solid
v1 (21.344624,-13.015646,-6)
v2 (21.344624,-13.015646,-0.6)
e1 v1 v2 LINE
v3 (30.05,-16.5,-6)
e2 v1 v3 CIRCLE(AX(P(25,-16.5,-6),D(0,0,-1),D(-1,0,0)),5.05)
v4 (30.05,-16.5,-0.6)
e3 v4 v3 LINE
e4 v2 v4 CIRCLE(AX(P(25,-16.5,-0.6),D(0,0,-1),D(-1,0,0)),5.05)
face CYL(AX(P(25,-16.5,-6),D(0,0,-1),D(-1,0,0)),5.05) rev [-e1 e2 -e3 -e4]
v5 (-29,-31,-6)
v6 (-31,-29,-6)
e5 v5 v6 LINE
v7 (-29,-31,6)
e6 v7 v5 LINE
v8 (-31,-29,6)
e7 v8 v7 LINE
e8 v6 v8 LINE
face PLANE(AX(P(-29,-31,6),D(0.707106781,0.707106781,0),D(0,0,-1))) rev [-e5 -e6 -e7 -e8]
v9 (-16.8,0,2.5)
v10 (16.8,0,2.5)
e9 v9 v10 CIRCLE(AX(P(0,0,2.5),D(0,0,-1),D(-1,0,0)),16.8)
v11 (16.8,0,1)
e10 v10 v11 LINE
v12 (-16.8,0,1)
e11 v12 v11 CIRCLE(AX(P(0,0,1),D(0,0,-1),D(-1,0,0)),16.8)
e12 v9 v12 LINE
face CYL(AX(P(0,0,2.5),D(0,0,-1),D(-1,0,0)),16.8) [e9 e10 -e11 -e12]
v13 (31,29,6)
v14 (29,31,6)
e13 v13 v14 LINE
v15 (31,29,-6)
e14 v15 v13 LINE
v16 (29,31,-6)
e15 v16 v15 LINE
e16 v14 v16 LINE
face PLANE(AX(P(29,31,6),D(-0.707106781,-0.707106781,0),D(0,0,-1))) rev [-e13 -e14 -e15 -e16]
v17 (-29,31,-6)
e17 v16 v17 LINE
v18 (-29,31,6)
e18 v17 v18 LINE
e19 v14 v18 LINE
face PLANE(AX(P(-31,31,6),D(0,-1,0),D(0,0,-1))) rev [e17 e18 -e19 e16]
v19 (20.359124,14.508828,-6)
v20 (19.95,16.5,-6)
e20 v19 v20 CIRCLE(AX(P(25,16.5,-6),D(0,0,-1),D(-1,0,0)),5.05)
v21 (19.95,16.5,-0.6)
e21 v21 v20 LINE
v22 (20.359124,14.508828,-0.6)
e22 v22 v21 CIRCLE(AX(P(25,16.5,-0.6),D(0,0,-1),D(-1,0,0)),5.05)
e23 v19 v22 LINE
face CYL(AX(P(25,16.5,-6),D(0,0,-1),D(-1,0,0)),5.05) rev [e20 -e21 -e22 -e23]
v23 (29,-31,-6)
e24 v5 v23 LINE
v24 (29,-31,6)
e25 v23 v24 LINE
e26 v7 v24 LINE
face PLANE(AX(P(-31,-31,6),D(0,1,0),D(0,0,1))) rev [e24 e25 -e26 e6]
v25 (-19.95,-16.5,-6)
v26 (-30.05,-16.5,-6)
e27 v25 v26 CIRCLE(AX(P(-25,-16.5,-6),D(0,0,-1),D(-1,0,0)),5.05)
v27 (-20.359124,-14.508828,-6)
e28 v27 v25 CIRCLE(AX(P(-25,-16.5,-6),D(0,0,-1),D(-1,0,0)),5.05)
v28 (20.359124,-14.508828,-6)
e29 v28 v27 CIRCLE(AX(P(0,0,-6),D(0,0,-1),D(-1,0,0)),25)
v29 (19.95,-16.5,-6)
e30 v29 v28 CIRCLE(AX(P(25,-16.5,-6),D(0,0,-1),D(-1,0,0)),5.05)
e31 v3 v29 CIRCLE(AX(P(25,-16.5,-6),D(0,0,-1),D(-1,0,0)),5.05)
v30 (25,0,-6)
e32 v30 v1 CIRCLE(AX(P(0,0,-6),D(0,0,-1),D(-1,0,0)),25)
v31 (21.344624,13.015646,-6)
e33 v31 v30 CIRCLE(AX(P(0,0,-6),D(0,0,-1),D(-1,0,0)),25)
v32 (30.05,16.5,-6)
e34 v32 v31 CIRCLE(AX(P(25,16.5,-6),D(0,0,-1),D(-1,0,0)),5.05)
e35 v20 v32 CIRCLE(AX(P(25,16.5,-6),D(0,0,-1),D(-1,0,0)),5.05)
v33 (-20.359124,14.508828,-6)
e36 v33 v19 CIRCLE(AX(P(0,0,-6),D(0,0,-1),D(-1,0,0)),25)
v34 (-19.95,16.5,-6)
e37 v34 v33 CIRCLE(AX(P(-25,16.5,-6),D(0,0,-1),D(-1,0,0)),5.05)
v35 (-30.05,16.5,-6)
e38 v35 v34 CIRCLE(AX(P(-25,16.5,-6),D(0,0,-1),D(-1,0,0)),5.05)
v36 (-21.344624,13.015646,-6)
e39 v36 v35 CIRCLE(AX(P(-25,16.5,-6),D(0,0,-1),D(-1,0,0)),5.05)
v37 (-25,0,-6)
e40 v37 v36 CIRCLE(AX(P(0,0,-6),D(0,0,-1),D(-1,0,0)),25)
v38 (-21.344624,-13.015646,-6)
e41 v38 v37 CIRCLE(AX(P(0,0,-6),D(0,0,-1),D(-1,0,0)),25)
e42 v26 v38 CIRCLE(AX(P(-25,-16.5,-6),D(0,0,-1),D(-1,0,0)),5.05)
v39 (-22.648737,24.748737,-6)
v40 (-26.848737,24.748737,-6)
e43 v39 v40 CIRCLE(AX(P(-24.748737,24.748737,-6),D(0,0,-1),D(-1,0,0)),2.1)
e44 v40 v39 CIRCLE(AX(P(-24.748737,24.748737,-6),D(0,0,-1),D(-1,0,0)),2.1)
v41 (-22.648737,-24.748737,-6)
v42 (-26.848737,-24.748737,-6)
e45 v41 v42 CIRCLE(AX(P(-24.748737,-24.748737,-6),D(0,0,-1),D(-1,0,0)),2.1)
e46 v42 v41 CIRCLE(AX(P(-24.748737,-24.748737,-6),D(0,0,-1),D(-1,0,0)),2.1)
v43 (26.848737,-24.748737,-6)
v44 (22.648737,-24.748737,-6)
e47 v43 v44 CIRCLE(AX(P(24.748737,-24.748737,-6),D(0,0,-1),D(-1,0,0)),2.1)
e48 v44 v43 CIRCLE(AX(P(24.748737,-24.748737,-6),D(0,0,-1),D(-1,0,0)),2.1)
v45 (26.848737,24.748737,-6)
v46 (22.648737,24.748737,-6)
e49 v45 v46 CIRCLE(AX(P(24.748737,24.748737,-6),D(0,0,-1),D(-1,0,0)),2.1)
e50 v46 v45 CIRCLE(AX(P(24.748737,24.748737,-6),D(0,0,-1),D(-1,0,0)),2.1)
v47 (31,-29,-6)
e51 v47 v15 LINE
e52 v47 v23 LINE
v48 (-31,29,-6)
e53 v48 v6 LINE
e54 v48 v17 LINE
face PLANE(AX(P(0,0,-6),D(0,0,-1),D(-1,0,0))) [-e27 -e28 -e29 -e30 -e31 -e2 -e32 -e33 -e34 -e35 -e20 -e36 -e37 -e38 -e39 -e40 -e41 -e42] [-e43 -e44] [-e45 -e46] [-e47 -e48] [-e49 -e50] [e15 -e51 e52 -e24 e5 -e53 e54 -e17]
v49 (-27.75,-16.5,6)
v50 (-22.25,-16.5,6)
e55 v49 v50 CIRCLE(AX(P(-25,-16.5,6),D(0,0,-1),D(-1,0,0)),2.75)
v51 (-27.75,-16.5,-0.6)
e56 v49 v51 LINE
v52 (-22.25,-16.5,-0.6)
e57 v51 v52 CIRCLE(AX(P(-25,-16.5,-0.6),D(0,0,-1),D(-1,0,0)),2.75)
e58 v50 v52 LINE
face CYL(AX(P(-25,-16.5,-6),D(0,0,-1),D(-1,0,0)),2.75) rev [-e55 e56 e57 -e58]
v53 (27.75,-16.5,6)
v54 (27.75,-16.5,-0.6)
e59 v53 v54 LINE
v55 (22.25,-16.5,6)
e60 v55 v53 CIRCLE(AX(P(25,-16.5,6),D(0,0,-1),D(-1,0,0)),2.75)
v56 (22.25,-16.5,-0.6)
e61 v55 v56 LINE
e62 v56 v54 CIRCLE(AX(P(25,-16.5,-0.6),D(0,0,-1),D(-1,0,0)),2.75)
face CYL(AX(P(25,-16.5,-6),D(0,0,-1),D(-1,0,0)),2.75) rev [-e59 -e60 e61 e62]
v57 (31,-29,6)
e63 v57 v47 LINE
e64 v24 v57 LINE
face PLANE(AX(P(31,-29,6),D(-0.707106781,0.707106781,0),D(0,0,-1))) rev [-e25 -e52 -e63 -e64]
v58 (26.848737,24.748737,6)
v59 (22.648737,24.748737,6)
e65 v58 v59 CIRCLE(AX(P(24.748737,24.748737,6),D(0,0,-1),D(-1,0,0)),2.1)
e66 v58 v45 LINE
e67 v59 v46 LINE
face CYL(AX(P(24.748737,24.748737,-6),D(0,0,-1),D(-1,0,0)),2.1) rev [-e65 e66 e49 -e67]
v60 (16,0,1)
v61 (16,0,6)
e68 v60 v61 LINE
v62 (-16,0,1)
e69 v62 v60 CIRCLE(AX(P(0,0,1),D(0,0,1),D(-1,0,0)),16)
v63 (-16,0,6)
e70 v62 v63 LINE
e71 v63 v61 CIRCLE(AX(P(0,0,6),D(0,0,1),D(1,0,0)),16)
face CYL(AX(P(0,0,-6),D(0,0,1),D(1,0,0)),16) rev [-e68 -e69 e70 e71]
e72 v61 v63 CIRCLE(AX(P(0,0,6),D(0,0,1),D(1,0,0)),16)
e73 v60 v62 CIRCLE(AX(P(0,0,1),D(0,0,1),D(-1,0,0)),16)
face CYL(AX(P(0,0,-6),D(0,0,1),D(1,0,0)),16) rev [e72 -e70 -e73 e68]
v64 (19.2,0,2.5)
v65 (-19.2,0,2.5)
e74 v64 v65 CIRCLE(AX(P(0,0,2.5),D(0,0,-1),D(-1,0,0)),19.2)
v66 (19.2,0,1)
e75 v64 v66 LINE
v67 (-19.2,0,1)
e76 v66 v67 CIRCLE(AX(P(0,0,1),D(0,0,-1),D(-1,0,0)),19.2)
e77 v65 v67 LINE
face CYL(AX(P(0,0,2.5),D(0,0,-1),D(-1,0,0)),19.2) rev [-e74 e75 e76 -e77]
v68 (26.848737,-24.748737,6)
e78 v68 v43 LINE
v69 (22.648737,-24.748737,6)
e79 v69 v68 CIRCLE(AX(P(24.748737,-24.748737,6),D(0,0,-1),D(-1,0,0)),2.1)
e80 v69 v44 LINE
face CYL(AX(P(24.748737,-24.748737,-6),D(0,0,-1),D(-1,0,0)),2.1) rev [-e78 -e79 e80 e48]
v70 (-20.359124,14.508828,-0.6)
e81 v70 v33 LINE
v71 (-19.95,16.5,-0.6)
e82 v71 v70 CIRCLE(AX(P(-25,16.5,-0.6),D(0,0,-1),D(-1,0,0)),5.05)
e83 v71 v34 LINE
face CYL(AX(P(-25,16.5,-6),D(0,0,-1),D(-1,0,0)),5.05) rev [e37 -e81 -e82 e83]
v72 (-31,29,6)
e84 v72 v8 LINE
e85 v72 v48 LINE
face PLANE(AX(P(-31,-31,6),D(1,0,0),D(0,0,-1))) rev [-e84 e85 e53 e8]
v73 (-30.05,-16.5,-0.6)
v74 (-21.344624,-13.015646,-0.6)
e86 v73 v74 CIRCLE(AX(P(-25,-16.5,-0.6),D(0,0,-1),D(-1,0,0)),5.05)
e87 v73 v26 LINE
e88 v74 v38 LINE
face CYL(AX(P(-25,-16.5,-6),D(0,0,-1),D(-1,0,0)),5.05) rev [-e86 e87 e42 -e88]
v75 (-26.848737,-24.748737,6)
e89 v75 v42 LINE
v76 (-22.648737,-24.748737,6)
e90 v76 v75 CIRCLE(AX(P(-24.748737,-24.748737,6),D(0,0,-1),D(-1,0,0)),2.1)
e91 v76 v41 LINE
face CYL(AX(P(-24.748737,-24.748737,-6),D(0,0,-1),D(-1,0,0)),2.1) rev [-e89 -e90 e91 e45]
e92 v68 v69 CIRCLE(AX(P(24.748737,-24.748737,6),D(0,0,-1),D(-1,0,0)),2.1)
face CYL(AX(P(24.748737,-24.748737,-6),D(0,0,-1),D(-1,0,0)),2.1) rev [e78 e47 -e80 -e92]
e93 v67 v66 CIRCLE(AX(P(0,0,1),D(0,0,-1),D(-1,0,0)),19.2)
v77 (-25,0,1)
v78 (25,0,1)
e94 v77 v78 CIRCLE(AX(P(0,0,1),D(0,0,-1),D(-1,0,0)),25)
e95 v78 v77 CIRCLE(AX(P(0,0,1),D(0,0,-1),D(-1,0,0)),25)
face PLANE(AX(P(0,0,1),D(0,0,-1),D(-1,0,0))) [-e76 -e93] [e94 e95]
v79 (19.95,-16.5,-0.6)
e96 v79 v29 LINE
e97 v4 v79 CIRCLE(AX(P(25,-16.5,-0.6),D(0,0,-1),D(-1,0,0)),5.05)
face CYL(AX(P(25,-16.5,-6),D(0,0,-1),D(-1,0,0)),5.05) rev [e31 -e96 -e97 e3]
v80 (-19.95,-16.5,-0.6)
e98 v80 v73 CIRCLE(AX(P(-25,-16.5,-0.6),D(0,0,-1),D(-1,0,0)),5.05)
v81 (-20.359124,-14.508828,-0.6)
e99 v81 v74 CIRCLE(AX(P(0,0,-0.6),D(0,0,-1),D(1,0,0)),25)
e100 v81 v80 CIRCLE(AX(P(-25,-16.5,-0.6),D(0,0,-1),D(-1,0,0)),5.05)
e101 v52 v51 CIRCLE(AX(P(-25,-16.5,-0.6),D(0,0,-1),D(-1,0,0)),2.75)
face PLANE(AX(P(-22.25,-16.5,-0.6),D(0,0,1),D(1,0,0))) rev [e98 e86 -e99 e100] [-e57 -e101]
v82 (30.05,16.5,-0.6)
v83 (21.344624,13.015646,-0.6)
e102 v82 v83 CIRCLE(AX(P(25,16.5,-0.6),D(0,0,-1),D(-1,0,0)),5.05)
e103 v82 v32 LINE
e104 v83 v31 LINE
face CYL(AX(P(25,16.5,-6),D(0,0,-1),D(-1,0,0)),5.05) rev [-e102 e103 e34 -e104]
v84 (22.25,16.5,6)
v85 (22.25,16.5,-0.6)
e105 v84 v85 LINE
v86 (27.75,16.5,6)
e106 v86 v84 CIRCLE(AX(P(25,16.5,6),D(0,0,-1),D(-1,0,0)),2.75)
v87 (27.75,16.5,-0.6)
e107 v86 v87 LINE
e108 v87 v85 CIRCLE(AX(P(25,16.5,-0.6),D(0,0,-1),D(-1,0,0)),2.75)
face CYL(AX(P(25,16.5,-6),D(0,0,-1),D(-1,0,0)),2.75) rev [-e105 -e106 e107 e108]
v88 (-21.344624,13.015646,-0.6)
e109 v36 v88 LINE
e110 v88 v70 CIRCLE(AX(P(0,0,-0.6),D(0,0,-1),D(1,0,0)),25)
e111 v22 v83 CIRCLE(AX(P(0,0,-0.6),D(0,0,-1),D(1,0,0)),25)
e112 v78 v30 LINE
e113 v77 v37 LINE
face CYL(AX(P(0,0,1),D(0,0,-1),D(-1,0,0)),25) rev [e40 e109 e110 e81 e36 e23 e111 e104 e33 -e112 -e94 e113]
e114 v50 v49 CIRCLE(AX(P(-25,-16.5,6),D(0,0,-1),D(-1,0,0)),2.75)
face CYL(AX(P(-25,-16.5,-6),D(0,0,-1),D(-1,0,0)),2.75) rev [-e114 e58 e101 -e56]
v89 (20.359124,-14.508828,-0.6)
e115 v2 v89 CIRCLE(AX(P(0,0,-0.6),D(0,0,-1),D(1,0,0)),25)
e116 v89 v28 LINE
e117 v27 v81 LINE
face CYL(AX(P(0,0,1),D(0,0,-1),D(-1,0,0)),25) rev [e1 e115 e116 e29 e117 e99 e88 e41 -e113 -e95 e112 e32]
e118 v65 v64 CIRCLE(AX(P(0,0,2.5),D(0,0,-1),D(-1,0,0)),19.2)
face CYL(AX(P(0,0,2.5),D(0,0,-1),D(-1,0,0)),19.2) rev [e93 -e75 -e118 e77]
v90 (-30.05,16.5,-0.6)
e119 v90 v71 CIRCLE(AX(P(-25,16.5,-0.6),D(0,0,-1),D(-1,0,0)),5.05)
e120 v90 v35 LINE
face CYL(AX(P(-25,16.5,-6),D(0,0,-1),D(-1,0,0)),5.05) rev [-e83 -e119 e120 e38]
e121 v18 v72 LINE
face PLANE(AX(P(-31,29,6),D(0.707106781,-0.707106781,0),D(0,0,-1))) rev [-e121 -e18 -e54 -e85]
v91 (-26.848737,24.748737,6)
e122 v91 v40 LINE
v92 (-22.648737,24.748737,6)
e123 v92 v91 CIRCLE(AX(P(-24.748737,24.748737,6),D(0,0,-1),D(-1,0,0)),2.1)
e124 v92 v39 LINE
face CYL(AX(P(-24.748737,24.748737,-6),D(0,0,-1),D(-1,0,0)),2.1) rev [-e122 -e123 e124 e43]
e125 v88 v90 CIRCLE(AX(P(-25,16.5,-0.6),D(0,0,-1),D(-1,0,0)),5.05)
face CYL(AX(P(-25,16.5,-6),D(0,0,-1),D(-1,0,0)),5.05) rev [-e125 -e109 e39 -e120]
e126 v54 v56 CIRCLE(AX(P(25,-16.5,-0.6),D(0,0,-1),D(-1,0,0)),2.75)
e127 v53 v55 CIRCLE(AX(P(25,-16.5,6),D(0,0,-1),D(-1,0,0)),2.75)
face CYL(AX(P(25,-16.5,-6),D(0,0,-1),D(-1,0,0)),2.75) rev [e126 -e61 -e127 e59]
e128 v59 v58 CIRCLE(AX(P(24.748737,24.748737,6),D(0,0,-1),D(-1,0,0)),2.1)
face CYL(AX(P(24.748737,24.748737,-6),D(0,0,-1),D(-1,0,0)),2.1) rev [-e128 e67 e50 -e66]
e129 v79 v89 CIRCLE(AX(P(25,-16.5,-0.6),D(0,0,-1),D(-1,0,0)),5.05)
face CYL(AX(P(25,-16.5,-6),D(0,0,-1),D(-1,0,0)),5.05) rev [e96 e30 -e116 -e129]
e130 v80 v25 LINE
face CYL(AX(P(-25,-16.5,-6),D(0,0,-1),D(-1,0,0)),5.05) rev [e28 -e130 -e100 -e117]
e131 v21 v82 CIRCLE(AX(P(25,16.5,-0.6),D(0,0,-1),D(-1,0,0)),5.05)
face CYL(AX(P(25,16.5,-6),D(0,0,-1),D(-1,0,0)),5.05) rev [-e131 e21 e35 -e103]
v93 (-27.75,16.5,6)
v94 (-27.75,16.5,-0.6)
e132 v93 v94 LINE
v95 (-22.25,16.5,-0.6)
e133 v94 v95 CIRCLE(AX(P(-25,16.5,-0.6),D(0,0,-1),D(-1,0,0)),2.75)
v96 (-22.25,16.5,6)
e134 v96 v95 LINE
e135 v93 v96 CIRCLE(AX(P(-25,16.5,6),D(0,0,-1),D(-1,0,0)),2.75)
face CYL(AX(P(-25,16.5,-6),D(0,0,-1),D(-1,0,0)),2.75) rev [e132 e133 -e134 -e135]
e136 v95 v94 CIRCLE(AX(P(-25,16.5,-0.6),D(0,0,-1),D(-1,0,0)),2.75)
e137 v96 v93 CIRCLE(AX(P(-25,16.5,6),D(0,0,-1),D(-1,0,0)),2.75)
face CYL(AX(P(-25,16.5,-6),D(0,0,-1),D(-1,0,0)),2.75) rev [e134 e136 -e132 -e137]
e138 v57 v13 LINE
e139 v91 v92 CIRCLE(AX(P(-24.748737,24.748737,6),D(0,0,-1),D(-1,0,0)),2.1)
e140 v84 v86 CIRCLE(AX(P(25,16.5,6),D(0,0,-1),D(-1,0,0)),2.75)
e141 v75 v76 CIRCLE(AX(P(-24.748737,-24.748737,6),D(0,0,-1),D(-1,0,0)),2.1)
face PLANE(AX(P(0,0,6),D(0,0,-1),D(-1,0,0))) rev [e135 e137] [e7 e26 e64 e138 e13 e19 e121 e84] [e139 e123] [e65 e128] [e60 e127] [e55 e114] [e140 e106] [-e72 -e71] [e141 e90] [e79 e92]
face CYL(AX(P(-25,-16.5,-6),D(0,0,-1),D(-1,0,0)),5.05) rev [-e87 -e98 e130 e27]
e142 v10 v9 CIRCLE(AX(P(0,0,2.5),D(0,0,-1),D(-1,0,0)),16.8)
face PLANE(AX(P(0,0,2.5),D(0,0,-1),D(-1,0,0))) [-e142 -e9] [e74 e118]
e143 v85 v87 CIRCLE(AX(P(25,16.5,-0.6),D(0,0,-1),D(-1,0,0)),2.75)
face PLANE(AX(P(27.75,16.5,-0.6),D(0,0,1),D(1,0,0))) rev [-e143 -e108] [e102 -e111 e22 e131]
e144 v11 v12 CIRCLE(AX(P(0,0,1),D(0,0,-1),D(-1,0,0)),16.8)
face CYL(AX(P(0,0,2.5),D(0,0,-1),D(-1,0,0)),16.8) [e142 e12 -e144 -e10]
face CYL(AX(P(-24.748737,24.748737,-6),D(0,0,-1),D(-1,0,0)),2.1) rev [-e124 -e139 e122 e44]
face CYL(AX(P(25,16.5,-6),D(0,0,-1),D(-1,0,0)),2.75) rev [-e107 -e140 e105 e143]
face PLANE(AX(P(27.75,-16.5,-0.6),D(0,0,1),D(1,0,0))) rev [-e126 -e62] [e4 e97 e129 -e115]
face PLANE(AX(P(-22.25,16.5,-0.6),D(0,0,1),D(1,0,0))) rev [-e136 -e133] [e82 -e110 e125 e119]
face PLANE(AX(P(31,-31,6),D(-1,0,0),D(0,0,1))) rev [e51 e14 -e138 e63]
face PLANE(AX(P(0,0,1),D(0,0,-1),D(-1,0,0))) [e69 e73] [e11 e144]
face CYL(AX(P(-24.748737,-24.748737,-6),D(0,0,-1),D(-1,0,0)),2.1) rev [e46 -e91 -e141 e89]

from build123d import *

# Parameters (mm, degrees)
SKETCH_1_W                     = 62
SKETCH_1_H                     = 62
EXTRUDE_1_DEPTH                = 6
SKETCH_2_R                     = 16
CUT_EXTRUDE_1_DEPTH            = 46.453272709
HOLE_WIZARD_M5_1_D             = 4.2
SKETCH_11_R                    = 25
CUT_EXTRUDE_2_DEPTH            = 7
HOLE_WIZARD_M5_1_2_D           = 5.5
HOLE_WIZARD_M5_1_2_CBORE_D     = 10.1
HOLE_WIZARD_M5_1_2_CBORE_DEPTH = 5.4
CHAMFER_1_SIZE                 = 2
SKETCH_13_R                    = 19.2
SKETCH_13_R_2                  = 16.8
CUT_EXTRUDE_3_DEPTH            = 1.5


with BuildPart() as part:
    # 草图1 → 凸台-拉伸1 (new, symmetric)
    with BuildSketch(Plane.XY):
        Rectangle(SKETCH_1_W, SKETCH_1_H)
    extrude(amount=EXTRUDE_1_DEPTH, both=True)

    # 草图2 → 切除-拉伸1 (cut, through all)
    with BuildSketch(Plane.XY.offset(6)):
        Circle(SKETCH_2_R)
    extrude(amount=-CUT_EXTRUDE_1_DEPTH, mode=Mode.SUBTRACT)

    # Hole Wizard M5 _1 (through all)
    with Locations(Plane(origin=(0, 0, -6), x_dir=(1, 0, 0), z_dir=(0, 0, -1))):
        with Locations((-24.748737342, -24.748737342), (24.748737342, -24.748737342), (-24.748737342, 24.748737342), (24.748737342, 24.748737342)):
            Hole(HOLE_WIZARD_M5_1_D / 2)

    # 草图11 → 切除-拉伸2 (cut)
    with BuildSketch(Plane(origin=(0, 0, -6), x_dir=(-1, 0, 0), z_dir=(0, 0, -1))):
        Circle(SKETCH_11_R)
    extrude(amount=-CUT_EXTRUDE_2_DEPTH, mode=Mode.SUBTRACT)

    # Hole Wizard M5 _1 2 (through all)
    with Locations(Plane(origin=(0, 0, -6), x_dir=(-1, 0, 0), z_dir=(0, 0, -1))):
        with Locations((-25, 16.5), (25, 16.5), (25, -16.5), (-25, -16.5)):
            CounterBoreHole(HOLE_WIZARD_M5_1_2_D / 2, HOLE_WIZARD_M5_1_2_CBORE_D / 2, HOLE_WIZARD_M5_1_2_CBORE_DEPTH)

    # 倒角1
    chamfer_1_edges = [part.edges().sort_by_distance(p)[0] for p in [
        (31, -31, 0),
        (-31, -31, 0),
        (-31, 31, 0),
        (31, 31, 0),
    ]]
    chamfer(chamfer_1_edges, length=CHAMFER_1_SIZE)

    # 草图13 → 切除-拉伸3 (cut)
    with BuildSketch(Plane(origin=(0, 0, 1), x_dir=(-1, 0, 0), z_dir=(0, 0, -1))):
        Circle(SKETCH_13_R)
        Circle(SKETCH_13_R_2, mode=Mode.SUBTRACT)
    extrude(amount=-CUT_EXTRUDE_3_DEPTH, mode=Mode.SUBTRACT)


solid = part.part
